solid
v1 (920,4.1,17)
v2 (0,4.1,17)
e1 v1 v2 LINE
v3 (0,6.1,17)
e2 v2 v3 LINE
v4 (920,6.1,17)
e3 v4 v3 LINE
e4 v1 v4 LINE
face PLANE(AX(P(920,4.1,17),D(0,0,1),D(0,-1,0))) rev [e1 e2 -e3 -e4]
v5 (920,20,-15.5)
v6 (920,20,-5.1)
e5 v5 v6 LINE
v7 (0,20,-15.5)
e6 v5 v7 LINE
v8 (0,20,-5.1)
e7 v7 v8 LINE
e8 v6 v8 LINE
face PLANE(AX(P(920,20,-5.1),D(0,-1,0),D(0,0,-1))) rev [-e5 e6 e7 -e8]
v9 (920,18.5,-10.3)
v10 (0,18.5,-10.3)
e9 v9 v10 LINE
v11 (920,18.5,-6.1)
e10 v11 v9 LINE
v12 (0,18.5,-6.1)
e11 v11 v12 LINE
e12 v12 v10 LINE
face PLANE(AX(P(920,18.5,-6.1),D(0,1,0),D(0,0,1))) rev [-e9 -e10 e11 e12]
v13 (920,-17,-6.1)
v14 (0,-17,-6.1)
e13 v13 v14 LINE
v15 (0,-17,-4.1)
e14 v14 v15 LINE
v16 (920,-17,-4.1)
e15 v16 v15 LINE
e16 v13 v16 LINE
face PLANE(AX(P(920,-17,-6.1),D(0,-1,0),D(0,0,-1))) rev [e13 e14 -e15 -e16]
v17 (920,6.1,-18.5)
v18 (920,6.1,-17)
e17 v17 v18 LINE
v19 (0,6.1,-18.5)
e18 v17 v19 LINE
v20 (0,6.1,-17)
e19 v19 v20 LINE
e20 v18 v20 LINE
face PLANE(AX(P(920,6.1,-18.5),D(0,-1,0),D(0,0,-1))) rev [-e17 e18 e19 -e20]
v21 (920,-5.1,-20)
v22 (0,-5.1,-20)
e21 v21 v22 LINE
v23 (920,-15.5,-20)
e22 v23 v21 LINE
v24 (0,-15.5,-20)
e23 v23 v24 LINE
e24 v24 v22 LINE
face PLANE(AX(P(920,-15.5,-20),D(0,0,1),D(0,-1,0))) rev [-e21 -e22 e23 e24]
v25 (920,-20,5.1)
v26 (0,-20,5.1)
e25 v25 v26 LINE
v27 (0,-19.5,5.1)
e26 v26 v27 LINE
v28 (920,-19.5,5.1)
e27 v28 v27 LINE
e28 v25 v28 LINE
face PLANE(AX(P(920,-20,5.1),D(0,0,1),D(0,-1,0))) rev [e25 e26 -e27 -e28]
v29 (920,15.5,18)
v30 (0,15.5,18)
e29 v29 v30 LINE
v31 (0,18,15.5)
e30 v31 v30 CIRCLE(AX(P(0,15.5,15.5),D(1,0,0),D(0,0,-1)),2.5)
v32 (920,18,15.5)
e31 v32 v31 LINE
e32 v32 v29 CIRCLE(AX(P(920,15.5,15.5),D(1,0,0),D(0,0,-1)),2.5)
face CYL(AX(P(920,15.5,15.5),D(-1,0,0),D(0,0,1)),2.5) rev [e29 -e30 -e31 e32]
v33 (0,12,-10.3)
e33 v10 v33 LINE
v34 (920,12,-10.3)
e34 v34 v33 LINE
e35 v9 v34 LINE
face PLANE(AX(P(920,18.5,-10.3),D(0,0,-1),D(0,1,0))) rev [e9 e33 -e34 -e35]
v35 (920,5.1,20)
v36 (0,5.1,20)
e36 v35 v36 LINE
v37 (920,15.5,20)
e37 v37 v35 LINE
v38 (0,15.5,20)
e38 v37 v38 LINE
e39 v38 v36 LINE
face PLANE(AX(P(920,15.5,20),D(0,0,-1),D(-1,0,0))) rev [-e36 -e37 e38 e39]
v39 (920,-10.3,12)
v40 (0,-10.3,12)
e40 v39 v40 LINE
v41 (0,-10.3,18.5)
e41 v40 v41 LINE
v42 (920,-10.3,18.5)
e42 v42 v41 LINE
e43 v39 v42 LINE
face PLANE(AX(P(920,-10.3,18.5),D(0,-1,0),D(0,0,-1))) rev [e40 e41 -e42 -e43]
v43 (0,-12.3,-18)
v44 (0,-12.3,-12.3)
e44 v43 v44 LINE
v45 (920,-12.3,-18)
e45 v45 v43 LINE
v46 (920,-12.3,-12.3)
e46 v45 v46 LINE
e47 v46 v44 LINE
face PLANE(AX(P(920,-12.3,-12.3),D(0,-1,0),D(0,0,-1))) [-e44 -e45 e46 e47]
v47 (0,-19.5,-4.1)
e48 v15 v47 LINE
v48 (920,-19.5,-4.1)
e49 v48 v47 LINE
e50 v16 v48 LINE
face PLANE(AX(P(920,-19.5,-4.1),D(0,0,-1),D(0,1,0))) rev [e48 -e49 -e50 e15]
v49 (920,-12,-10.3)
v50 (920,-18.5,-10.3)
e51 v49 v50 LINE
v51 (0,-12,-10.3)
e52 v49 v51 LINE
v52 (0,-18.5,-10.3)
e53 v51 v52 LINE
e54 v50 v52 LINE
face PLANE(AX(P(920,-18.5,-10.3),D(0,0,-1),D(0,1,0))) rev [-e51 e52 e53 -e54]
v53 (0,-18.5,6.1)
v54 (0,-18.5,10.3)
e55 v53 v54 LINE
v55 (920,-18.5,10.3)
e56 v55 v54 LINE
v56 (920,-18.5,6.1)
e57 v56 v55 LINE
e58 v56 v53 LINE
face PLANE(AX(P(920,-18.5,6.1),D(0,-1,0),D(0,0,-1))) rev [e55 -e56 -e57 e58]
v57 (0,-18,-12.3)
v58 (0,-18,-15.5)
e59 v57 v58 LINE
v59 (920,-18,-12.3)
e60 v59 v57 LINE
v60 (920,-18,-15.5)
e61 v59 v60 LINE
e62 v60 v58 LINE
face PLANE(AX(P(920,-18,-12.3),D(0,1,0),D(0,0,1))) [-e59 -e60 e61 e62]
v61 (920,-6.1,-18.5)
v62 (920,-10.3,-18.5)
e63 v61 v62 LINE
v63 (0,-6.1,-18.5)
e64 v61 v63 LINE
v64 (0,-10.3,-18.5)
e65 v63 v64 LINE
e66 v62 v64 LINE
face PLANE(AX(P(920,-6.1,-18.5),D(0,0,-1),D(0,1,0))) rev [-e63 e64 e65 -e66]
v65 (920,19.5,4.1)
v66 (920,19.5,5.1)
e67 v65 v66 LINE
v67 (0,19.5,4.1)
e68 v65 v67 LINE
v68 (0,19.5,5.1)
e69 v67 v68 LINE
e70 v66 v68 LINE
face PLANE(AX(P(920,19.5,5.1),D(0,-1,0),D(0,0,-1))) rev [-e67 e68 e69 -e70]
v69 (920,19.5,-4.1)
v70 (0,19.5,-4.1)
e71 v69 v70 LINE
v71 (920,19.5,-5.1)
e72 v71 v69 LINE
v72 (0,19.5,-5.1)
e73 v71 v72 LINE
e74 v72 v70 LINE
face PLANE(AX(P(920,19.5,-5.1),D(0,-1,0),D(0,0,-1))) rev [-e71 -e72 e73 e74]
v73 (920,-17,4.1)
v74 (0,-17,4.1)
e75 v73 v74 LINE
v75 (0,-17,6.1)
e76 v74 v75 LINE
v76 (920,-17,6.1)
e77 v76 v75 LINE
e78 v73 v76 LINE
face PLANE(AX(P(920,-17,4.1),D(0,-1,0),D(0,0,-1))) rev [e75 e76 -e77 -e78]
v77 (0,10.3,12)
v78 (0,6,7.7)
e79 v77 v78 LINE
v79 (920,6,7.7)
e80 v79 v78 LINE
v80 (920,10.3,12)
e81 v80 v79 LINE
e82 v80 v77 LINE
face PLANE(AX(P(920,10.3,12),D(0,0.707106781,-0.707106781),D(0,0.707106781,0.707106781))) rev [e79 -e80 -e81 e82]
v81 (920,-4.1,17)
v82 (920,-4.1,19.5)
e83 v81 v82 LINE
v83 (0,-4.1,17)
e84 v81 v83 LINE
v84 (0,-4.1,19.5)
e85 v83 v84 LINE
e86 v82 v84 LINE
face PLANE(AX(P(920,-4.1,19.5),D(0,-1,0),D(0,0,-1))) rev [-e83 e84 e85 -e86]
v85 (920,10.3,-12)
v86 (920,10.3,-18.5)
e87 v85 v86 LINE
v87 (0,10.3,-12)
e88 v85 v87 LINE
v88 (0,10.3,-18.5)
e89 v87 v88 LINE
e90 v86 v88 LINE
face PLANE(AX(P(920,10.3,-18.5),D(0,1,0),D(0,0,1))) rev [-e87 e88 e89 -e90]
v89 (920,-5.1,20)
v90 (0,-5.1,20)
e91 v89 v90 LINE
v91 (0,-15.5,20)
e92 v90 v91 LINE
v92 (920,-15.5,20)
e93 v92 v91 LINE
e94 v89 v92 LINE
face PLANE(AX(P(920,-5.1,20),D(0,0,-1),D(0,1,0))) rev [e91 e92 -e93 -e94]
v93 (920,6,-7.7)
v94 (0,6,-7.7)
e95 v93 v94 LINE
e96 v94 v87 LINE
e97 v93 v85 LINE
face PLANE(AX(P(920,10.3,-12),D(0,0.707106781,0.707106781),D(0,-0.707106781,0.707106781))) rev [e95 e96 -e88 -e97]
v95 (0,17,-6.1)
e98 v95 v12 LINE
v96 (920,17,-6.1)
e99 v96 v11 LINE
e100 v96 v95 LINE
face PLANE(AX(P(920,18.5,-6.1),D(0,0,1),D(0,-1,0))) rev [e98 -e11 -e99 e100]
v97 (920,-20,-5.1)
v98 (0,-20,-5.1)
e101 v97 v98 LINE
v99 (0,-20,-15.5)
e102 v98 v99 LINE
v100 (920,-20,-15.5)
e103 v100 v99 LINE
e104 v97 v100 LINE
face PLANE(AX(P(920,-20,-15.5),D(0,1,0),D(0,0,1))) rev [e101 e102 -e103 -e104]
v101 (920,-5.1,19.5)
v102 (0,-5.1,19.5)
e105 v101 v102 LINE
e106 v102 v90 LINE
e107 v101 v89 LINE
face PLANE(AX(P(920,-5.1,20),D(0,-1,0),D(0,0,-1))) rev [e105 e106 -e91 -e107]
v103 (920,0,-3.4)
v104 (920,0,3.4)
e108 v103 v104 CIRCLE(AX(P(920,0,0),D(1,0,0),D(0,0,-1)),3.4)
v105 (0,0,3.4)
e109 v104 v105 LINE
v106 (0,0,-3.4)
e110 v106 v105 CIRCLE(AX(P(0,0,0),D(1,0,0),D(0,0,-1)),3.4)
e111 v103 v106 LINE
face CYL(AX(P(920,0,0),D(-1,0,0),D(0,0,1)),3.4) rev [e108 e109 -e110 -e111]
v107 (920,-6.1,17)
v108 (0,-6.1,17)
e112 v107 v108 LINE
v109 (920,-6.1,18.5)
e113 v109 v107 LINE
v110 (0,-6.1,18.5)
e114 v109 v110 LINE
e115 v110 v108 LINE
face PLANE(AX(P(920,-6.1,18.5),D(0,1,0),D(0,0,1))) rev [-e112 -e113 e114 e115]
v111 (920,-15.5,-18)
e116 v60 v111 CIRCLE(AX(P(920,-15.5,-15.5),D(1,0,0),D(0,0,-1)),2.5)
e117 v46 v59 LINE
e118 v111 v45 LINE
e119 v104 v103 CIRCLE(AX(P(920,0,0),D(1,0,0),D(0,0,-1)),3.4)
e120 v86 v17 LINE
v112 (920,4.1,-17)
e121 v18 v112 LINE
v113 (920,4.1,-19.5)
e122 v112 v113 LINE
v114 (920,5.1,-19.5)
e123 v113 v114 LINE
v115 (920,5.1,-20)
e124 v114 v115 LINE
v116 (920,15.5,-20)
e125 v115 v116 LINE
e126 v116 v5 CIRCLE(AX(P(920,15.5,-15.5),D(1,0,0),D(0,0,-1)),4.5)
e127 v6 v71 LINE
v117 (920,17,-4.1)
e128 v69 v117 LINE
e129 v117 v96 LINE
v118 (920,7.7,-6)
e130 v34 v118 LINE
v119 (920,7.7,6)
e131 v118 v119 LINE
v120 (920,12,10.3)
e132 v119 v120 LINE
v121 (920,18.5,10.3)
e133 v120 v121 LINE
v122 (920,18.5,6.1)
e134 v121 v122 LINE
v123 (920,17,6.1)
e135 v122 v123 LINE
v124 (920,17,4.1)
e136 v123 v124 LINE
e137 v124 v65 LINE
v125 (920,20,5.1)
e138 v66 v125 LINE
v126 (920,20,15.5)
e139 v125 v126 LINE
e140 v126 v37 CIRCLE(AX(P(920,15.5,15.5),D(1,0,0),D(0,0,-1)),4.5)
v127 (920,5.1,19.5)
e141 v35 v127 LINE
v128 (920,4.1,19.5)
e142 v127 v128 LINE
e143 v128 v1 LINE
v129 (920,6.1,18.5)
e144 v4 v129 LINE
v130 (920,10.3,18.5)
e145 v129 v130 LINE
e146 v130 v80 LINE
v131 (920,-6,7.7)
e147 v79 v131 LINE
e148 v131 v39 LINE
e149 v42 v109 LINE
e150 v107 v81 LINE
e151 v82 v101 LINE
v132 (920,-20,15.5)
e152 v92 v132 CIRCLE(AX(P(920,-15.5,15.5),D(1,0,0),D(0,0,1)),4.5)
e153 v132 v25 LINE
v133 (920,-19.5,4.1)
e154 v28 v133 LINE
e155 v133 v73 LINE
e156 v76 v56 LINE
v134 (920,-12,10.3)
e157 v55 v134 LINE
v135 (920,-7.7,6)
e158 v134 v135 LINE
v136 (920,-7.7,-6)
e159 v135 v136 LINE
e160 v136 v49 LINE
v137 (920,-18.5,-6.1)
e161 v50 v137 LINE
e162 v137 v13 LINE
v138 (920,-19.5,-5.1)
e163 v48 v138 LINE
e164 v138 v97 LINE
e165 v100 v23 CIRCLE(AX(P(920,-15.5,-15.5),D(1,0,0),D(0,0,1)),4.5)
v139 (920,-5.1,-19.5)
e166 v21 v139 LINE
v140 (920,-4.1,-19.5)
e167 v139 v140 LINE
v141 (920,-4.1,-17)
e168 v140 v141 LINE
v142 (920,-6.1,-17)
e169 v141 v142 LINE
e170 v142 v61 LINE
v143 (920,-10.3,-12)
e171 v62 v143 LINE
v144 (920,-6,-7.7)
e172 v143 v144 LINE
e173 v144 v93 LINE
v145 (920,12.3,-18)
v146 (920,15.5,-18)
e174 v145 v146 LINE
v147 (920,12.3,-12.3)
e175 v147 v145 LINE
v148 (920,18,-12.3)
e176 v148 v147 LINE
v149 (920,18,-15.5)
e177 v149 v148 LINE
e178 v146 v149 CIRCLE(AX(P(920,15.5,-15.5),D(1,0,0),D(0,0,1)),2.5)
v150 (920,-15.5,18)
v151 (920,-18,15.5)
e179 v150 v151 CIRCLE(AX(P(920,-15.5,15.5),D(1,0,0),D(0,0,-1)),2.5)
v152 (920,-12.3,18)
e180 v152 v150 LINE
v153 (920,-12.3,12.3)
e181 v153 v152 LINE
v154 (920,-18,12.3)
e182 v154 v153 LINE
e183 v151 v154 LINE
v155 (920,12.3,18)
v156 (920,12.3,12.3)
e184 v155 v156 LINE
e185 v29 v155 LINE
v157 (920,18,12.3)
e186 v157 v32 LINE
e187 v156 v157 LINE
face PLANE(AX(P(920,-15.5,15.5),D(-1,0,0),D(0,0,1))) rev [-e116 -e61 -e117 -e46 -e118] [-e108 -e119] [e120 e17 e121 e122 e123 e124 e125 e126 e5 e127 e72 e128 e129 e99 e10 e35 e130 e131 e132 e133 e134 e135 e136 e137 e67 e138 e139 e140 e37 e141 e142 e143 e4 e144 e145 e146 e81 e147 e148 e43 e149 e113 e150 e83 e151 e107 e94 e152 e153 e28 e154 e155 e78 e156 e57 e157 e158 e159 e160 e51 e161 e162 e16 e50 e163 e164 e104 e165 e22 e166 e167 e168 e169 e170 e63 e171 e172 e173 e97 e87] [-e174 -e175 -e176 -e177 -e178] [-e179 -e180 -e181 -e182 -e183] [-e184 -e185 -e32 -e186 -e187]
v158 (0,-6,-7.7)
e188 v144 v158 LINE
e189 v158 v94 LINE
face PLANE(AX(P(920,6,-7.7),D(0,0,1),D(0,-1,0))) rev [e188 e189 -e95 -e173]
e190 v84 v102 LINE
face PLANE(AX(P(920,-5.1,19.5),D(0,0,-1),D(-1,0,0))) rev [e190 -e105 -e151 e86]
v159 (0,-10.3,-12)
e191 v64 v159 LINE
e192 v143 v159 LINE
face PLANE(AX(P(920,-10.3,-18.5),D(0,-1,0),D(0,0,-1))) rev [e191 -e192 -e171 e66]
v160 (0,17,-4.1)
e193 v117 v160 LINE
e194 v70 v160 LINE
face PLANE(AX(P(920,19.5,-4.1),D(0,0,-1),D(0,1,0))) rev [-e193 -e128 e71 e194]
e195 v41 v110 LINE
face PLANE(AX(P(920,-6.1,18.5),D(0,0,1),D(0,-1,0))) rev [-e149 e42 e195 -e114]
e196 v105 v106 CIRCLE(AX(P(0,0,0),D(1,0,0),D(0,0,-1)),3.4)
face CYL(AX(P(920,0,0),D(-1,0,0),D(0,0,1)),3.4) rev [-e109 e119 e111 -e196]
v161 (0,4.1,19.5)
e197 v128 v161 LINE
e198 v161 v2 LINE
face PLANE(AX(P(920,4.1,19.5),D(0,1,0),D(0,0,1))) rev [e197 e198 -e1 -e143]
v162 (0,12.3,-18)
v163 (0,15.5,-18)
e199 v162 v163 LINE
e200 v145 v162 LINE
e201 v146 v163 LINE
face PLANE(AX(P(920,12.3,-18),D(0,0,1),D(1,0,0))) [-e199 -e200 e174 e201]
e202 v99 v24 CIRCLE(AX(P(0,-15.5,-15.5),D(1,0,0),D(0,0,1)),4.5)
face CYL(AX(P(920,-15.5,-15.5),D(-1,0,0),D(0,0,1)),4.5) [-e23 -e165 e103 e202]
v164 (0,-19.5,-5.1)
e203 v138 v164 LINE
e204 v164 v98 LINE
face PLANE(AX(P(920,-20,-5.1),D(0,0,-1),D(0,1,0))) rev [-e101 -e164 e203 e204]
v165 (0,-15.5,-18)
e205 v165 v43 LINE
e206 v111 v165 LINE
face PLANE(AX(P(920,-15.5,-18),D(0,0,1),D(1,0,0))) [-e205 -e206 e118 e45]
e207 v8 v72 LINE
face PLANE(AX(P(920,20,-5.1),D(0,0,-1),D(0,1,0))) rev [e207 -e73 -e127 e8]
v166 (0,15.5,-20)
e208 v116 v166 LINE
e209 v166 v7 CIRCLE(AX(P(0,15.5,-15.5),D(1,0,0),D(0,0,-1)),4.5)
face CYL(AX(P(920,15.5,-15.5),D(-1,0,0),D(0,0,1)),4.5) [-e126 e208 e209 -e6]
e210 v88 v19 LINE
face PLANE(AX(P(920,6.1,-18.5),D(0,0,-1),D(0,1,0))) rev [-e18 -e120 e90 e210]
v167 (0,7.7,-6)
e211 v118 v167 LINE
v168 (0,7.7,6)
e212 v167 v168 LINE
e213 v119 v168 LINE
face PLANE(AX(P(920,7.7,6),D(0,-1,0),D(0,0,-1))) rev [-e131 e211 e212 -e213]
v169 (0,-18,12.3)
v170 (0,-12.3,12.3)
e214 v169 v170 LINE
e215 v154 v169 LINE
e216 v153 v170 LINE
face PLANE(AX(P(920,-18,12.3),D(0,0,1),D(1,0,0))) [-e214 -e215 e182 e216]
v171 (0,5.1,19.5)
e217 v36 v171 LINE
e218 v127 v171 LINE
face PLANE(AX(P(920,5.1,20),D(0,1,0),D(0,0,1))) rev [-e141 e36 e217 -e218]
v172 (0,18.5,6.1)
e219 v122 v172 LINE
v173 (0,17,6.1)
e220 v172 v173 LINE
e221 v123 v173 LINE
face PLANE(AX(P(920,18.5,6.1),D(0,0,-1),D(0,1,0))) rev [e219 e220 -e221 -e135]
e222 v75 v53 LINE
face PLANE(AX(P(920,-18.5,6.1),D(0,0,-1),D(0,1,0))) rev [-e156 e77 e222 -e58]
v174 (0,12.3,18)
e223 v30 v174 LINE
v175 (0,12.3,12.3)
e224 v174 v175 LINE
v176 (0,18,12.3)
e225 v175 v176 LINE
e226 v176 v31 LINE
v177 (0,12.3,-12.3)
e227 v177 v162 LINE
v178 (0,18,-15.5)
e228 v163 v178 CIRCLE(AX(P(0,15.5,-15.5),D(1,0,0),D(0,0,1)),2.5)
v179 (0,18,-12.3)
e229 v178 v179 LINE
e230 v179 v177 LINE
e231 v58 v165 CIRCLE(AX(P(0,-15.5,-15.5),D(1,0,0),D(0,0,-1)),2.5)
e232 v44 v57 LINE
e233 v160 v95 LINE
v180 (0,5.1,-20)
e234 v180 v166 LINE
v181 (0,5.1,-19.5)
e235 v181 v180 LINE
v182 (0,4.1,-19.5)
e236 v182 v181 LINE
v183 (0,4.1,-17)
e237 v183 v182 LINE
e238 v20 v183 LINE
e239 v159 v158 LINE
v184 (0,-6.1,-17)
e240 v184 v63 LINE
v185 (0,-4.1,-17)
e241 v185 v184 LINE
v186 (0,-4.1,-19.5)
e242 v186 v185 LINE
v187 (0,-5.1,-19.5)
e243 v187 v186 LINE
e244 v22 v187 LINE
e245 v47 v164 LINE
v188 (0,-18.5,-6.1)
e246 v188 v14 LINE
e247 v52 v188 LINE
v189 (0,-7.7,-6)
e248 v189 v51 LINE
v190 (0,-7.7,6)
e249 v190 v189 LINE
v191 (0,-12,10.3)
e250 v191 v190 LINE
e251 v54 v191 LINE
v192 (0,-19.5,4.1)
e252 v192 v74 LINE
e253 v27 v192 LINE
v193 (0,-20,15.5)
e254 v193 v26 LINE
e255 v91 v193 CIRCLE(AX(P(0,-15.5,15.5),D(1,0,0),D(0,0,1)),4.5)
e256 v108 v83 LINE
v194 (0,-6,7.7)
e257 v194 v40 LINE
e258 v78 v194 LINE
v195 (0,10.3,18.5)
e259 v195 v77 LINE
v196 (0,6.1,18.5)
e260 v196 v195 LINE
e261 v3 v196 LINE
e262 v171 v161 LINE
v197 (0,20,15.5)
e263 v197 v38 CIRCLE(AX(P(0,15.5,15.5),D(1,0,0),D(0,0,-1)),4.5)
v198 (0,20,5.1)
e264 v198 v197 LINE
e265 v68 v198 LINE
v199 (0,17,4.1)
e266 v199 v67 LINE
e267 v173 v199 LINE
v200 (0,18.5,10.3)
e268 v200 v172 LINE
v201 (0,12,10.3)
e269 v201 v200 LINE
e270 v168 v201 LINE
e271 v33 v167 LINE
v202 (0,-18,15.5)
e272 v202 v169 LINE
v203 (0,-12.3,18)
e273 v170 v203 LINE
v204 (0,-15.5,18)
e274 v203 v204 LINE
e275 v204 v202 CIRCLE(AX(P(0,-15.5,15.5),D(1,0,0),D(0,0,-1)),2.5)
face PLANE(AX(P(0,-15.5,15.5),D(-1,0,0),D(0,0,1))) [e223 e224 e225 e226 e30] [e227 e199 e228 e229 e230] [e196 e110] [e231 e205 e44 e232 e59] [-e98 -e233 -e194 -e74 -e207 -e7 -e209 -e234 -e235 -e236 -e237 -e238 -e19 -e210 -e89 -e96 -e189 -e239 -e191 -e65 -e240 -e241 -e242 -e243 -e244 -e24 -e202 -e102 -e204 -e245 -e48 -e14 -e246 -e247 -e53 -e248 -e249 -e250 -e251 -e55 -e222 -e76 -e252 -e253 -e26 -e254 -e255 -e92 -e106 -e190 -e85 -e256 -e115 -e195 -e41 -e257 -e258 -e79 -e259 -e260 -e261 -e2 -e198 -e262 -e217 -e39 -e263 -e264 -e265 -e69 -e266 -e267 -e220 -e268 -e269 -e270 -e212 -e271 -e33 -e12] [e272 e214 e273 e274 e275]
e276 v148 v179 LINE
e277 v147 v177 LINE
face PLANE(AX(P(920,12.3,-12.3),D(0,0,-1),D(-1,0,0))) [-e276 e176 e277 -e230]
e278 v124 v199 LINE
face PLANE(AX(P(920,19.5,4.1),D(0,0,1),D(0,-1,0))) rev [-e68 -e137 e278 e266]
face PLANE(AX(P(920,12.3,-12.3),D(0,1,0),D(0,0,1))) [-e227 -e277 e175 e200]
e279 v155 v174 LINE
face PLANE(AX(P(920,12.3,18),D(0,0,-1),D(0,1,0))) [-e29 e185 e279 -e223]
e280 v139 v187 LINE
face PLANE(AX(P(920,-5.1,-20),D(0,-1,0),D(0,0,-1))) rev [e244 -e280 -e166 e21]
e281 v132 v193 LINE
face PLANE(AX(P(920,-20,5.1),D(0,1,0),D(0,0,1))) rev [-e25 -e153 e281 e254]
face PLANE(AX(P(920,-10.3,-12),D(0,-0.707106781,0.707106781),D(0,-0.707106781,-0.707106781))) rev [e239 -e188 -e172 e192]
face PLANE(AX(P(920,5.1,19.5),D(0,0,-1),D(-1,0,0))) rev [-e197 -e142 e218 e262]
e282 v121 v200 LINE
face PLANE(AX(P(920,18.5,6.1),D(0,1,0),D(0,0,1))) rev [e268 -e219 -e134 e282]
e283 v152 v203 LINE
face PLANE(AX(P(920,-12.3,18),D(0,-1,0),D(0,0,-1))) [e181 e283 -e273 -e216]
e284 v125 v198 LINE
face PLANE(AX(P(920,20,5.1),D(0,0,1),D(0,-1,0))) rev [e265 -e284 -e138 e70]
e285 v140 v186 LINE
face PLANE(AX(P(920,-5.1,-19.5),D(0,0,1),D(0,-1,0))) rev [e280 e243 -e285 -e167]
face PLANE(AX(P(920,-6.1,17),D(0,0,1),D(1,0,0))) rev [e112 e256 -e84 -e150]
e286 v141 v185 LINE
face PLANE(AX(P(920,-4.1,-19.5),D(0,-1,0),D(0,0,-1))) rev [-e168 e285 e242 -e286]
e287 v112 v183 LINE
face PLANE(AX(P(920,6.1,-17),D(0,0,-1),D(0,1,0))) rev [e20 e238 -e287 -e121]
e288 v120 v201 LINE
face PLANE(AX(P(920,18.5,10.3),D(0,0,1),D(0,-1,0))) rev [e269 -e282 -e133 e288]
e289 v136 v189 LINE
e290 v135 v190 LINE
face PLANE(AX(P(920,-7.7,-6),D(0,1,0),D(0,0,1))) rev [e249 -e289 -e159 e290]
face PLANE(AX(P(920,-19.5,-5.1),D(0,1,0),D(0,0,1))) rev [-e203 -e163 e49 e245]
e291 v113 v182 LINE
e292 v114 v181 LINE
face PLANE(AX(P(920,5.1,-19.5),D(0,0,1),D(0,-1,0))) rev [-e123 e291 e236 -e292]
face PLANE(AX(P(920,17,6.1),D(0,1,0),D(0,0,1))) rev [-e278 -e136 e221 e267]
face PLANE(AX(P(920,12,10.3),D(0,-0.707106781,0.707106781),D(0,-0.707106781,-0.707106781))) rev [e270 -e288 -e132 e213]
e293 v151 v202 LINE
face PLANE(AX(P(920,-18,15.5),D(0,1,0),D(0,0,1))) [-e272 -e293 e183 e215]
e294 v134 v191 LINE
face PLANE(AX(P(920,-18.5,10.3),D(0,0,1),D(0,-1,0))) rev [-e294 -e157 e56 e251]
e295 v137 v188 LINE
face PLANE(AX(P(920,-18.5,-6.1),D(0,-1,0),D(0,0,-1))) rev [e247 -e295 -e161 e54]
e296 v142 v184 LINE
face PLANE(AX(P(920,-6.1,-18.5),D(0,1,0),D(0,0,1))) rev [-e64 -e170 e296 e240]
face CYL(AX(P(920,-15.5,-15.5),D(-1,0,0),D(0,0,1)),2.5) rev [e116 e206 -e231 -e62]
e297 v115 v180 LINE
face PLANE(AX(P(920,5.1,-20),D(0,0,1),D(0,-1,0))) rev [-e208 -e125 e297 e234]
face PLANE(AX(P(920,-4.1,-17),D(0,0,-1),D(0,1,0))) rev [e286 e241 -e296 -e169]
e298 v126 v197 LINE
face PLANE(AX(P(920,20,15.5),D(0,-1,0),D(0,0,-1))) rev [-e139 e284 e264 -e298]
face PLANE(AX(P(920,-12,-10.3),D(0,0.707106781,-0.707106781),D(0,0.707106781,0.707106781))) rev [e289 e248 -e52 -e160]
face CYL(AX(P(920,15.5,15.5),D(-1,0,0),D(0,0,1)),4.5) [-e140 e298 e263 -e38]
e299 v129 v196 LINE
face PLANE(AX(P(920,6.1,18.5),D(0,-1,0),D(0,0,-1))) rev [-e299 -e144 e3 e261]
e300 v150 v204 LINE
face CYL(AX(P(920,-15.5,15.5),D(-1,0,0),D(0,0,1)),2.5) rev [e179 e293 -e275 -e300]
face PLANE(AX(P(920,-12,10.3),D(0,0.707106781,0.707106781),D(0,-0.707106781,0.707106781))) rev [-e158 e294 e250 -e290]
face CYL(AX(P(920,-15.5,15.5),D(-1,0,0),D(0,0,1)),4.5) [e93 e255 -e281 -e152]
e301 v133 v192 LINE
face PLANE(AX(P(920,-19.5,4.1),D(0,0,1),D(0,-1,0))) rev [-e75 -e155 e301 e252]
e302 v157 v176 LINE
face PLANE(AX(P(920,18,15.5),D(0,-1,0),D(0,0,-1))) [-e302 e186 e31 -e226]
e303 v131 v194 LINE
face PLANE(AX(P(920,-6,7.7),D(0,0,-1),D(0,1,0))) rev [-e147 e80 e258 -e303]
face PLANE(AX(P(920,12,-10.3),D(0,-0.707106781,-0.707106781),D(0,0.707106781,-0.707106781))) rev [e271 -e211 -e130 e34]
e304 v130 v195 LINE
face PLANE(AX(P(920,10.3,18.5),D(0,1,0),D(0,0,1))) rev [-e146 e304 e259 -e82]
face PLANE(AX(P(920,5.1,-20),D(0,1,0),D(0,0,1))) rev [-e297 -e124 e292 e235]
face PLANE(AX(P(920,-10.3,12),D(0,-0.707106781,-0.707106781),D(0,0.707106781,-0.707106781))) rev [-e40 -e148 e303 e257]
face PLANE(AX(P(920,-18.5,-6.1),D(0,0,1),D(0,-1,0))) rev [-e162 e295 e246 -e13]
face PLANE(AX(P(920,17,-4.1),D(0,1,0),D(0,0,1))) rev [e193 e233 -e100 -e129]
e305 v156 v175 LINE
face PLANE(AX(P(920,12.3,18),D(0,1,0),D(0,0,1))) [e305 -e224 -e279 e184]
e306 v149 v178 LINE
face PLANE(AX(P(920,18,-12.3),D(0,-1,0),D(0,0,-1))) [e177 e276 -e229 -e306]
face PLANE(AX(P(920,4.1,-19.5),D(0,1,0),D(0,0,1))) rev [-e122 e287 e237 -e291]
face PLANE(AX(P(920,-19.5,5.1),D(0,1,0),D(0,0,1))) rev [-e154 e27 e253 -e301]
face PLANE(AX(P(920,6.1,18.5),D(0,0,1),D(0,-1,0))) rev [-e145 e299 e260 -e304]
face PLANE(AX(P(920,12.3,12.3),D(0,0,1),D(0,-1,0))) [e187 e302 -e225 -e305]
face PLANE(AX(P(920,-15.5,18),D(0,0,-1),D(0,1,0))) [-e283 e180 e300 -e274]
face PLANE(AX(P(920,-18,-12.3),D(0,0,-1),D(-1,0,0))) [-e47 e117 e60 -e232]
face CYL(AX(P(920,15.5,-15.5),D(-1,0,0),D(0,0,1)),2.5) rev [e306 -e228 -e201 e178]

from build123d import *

# Parameters (mm, degrees)
SKETCH1_R                                = 3.4
ALUMINUM_PROFILE_40_X_40B_X_R4_5_1_DEPTH = 920


with BuildPart() as part:
    # Sketch1 → Aluminum profile 40 X 40B X R4.5(1) (new body)
    with BuildSketch(Plane.YZ):
        with BuildLine():
            Line((-5.1, 20), (-5.1, 19.5))
            Line((-5.1, 19.5), (-4.1, 19.5))
            Line((-4.1, 19.5), (-4.1, 17))
            Line((-4.1, 17), (-6.1, 17))
            Line((-6.1, 17), (-6.1, 18.5))
            Line((-6.1, 18.5), (-10.3, 18.5))
            Line((-10.3, 18.5), (-10.3, 12))
            Line((-10.3, 12), (-6, 7.7))
            Line((-6, 7.7), (6, 7.7))
            Line((6, 7.7), (10.3, 12))
            Line((10.3, 12), (10.3, 18.5))
            Line((10.3, 18.5), (6.1, 18.5))
            Line((6.1, 18.5), (6.1, 17))
            Line((6.1, 17), (4.1, 17))
            Line((4.1, 17), (4.1, 19.5))
            Line((4.1, 19.5), (5.1, 19.5))
            Line((5.1, 19.5), (5.1, 20))
            Line((5.1, 20), (15.5, 20))
            ThreePointArc((15.5, 20), (18.681980515, 18.681980515), (20, 15.5))
            Line((20, 15.5), (20, 5.1))
            Line((20, 5.1), (19.5, 5.1))
            Line((19.5, 5.1), (19.5, 4.1))
            Line((19.5, 4.1), (17, 4.1))
            Line((17, 4.1), (17, 6.1))
            Line((17, 6.1), (18.5, 6.1))
            Line((18.5, 6.1), (18.5, 10.3))
            Line((18.5, 10.3), (12, 10.3))
            Line((12, 10.3), (7.7, 6))
            Line((7.7, 6), (7.7, -6))
            Line((7.7, -6), (12, -10.3))
            Line((12, -10.3), (18.5, -10.3))
            Line((18.5, -10.3), (18.5, -6.1))
            Line((18.5, -6.1), (17, -6.1))
            Line((17, -6.1), (17, -4.1))
            Line((17, -4.1), (19.5, -4.1))
            Line((19.5, -4.1), (19.5, -5.1))
            Line((19.5, -5.1), (20, -5.1))
            Line((20, -5.1), (20, -15.5))
            ThreePointArc((20, -15.5), (18.681980515, -18.681980515), (15.5, -20))
            Line((15.5, -20), (5.1, -20))
            Line((5.1, -20), (5.1, -19.5))
            Line((5.1, -19.5), (4.1, -19.5))
            Line((4.1, -19.5), (4.1, -17))
            Line((4.1, -17), (6.1, -17))
            Line((6.1, -17), (6.1, -18.5))
            Line((6.1, -18.5), (10.3, -18.5))
            Line((10.3, -18.5), (10.3, -12))
            Line((10.3, -12), (6, -7.7))
            Line((6, -7.7), (-6, -7.7))
            Line((-6, -7.7), (-10.3, -12))
            Line((-10.3, -12), (-10.3, -18.5))
            Line((-10.3, -18.5), (-6.1, -18.5))
            Line((-6.1, -18.5), (-6.1, -17))
            Line((-6.1, -17), (-4.1, -17))
            Line((-4.1, -17), (-4.1, -19.5))
            Line((-4.1, -19.5), (-5.1, -19.5))
            Line((-5.1, -19.5), (-5.1, -20))
            Line((-5.1, -20), (-15.5, -20))
            ThreePointArc((-15.5, -20), (-18.681980515, -18.681980515), (-20, -15.5))
            Line((-20, -15.5), (-20, -5.1))
            Line((-20, -5.1), (-19.5, -5.1))
            Line((-19.5, -5.1), (-19.5, -4.1))
            Line((-19.5, -4.1), (-17, -4.1))
            Line((-17, -4.1), (-17, -6.1))
            Line((-17, -6.1), (-18.5, -6.1))
            Line((-18.5, -6.1), (-18.5, -10.3))
            Line((-18.5, -10.3), (-12, -10.3))
            Line((-12, -10.3), (-7.7, -6))
            Line((-7.7, -6), (-7.7, 6))
            Line((-7.7, 6), (-12, 10.3))
            Line((-12, 10.3), (-18.5, 10.3))
            Line((-18.5, 10.3), (-18.5, 6.1))
            Line((-18.5, 6.1), (-17, 6.1))
            Line((-17, 6.1), (-17, 4.1))
            Line((-17, 4.1), (-19.5, 4.1))
            Line((-19.5, 4.1), (-19.5, 5.1))
            Line((-19.5, 5.1), (-20, 5.1))
            Line((-20, 5.1), (-20, 15.5))
            ThreePointArc((-20, 15.5), (-18.681980515, 18.681980515), (-15.5, 20))
            Line((-15.5, 20), (-5.1, 20))
        make_face()
        Circle(SKETCH1_R, mode=Mode.SUBTRACT)
        with BuildLine():
            Line((12.3, 18), (15.5, 18))
            ThreePointArc((15.5, 18), (17.267766953, 17.267766953), (18, 15.5))
            Line((18, 15.5), (18, 12.3))
            Line((18, 12.3), (12.3, 12.3))
            Line((12.3, 12.3), (12.3, 18))
        make_face(mode=Mode.SUBTRACT)
        with BuildLine():
            Line((-15.5, 18), (-12.3, 18))
            Line((-12.3, 18), (-12.3, 12.3))
            Line((-12.3, 12.3), (-18, 12.3))
            Line((-18, 12.3), (-18, 15.5))
            ThreePointArc((-18, 15.5), (-17.267766953, 17.267766953), (-15.5, 18))
        make_face(mode=Mode.SUBTRACT)
        with BuildLine():
            Line((-18, -12.3), (-12.3, -12.3))
            Line((-12.3, -12.3), (-12.3, -18))
            Line((-12.3, -18), (-15.5, -18))
            ThreePointArc((-15.5, -18), (-17.267766953, -17.267766953), (-18, -15.5))
            Line((-18, -15.5), (-18, -12.3))
        make_face(mode=Mode.SUBTRACT)
        with BuildLine():
            Line((12.3, -12.3), (18, -12.3))
            Line((18, -12.3), (18, -15.5))
            ThreePointArc((18, -15.5), (17.267766953, -17.267766953), (15.5, -18))
            Line((15.5, -18), (12.3, -18))
            Line((12.3, -18), (12.3, -12.3))
        make_face(mode=Mode.SUBTRACT)
    extrude(amount=ALUMINUM_PROFILE_40_X_40B_X_R4_5_1_DEPTH)


solid = part.part
